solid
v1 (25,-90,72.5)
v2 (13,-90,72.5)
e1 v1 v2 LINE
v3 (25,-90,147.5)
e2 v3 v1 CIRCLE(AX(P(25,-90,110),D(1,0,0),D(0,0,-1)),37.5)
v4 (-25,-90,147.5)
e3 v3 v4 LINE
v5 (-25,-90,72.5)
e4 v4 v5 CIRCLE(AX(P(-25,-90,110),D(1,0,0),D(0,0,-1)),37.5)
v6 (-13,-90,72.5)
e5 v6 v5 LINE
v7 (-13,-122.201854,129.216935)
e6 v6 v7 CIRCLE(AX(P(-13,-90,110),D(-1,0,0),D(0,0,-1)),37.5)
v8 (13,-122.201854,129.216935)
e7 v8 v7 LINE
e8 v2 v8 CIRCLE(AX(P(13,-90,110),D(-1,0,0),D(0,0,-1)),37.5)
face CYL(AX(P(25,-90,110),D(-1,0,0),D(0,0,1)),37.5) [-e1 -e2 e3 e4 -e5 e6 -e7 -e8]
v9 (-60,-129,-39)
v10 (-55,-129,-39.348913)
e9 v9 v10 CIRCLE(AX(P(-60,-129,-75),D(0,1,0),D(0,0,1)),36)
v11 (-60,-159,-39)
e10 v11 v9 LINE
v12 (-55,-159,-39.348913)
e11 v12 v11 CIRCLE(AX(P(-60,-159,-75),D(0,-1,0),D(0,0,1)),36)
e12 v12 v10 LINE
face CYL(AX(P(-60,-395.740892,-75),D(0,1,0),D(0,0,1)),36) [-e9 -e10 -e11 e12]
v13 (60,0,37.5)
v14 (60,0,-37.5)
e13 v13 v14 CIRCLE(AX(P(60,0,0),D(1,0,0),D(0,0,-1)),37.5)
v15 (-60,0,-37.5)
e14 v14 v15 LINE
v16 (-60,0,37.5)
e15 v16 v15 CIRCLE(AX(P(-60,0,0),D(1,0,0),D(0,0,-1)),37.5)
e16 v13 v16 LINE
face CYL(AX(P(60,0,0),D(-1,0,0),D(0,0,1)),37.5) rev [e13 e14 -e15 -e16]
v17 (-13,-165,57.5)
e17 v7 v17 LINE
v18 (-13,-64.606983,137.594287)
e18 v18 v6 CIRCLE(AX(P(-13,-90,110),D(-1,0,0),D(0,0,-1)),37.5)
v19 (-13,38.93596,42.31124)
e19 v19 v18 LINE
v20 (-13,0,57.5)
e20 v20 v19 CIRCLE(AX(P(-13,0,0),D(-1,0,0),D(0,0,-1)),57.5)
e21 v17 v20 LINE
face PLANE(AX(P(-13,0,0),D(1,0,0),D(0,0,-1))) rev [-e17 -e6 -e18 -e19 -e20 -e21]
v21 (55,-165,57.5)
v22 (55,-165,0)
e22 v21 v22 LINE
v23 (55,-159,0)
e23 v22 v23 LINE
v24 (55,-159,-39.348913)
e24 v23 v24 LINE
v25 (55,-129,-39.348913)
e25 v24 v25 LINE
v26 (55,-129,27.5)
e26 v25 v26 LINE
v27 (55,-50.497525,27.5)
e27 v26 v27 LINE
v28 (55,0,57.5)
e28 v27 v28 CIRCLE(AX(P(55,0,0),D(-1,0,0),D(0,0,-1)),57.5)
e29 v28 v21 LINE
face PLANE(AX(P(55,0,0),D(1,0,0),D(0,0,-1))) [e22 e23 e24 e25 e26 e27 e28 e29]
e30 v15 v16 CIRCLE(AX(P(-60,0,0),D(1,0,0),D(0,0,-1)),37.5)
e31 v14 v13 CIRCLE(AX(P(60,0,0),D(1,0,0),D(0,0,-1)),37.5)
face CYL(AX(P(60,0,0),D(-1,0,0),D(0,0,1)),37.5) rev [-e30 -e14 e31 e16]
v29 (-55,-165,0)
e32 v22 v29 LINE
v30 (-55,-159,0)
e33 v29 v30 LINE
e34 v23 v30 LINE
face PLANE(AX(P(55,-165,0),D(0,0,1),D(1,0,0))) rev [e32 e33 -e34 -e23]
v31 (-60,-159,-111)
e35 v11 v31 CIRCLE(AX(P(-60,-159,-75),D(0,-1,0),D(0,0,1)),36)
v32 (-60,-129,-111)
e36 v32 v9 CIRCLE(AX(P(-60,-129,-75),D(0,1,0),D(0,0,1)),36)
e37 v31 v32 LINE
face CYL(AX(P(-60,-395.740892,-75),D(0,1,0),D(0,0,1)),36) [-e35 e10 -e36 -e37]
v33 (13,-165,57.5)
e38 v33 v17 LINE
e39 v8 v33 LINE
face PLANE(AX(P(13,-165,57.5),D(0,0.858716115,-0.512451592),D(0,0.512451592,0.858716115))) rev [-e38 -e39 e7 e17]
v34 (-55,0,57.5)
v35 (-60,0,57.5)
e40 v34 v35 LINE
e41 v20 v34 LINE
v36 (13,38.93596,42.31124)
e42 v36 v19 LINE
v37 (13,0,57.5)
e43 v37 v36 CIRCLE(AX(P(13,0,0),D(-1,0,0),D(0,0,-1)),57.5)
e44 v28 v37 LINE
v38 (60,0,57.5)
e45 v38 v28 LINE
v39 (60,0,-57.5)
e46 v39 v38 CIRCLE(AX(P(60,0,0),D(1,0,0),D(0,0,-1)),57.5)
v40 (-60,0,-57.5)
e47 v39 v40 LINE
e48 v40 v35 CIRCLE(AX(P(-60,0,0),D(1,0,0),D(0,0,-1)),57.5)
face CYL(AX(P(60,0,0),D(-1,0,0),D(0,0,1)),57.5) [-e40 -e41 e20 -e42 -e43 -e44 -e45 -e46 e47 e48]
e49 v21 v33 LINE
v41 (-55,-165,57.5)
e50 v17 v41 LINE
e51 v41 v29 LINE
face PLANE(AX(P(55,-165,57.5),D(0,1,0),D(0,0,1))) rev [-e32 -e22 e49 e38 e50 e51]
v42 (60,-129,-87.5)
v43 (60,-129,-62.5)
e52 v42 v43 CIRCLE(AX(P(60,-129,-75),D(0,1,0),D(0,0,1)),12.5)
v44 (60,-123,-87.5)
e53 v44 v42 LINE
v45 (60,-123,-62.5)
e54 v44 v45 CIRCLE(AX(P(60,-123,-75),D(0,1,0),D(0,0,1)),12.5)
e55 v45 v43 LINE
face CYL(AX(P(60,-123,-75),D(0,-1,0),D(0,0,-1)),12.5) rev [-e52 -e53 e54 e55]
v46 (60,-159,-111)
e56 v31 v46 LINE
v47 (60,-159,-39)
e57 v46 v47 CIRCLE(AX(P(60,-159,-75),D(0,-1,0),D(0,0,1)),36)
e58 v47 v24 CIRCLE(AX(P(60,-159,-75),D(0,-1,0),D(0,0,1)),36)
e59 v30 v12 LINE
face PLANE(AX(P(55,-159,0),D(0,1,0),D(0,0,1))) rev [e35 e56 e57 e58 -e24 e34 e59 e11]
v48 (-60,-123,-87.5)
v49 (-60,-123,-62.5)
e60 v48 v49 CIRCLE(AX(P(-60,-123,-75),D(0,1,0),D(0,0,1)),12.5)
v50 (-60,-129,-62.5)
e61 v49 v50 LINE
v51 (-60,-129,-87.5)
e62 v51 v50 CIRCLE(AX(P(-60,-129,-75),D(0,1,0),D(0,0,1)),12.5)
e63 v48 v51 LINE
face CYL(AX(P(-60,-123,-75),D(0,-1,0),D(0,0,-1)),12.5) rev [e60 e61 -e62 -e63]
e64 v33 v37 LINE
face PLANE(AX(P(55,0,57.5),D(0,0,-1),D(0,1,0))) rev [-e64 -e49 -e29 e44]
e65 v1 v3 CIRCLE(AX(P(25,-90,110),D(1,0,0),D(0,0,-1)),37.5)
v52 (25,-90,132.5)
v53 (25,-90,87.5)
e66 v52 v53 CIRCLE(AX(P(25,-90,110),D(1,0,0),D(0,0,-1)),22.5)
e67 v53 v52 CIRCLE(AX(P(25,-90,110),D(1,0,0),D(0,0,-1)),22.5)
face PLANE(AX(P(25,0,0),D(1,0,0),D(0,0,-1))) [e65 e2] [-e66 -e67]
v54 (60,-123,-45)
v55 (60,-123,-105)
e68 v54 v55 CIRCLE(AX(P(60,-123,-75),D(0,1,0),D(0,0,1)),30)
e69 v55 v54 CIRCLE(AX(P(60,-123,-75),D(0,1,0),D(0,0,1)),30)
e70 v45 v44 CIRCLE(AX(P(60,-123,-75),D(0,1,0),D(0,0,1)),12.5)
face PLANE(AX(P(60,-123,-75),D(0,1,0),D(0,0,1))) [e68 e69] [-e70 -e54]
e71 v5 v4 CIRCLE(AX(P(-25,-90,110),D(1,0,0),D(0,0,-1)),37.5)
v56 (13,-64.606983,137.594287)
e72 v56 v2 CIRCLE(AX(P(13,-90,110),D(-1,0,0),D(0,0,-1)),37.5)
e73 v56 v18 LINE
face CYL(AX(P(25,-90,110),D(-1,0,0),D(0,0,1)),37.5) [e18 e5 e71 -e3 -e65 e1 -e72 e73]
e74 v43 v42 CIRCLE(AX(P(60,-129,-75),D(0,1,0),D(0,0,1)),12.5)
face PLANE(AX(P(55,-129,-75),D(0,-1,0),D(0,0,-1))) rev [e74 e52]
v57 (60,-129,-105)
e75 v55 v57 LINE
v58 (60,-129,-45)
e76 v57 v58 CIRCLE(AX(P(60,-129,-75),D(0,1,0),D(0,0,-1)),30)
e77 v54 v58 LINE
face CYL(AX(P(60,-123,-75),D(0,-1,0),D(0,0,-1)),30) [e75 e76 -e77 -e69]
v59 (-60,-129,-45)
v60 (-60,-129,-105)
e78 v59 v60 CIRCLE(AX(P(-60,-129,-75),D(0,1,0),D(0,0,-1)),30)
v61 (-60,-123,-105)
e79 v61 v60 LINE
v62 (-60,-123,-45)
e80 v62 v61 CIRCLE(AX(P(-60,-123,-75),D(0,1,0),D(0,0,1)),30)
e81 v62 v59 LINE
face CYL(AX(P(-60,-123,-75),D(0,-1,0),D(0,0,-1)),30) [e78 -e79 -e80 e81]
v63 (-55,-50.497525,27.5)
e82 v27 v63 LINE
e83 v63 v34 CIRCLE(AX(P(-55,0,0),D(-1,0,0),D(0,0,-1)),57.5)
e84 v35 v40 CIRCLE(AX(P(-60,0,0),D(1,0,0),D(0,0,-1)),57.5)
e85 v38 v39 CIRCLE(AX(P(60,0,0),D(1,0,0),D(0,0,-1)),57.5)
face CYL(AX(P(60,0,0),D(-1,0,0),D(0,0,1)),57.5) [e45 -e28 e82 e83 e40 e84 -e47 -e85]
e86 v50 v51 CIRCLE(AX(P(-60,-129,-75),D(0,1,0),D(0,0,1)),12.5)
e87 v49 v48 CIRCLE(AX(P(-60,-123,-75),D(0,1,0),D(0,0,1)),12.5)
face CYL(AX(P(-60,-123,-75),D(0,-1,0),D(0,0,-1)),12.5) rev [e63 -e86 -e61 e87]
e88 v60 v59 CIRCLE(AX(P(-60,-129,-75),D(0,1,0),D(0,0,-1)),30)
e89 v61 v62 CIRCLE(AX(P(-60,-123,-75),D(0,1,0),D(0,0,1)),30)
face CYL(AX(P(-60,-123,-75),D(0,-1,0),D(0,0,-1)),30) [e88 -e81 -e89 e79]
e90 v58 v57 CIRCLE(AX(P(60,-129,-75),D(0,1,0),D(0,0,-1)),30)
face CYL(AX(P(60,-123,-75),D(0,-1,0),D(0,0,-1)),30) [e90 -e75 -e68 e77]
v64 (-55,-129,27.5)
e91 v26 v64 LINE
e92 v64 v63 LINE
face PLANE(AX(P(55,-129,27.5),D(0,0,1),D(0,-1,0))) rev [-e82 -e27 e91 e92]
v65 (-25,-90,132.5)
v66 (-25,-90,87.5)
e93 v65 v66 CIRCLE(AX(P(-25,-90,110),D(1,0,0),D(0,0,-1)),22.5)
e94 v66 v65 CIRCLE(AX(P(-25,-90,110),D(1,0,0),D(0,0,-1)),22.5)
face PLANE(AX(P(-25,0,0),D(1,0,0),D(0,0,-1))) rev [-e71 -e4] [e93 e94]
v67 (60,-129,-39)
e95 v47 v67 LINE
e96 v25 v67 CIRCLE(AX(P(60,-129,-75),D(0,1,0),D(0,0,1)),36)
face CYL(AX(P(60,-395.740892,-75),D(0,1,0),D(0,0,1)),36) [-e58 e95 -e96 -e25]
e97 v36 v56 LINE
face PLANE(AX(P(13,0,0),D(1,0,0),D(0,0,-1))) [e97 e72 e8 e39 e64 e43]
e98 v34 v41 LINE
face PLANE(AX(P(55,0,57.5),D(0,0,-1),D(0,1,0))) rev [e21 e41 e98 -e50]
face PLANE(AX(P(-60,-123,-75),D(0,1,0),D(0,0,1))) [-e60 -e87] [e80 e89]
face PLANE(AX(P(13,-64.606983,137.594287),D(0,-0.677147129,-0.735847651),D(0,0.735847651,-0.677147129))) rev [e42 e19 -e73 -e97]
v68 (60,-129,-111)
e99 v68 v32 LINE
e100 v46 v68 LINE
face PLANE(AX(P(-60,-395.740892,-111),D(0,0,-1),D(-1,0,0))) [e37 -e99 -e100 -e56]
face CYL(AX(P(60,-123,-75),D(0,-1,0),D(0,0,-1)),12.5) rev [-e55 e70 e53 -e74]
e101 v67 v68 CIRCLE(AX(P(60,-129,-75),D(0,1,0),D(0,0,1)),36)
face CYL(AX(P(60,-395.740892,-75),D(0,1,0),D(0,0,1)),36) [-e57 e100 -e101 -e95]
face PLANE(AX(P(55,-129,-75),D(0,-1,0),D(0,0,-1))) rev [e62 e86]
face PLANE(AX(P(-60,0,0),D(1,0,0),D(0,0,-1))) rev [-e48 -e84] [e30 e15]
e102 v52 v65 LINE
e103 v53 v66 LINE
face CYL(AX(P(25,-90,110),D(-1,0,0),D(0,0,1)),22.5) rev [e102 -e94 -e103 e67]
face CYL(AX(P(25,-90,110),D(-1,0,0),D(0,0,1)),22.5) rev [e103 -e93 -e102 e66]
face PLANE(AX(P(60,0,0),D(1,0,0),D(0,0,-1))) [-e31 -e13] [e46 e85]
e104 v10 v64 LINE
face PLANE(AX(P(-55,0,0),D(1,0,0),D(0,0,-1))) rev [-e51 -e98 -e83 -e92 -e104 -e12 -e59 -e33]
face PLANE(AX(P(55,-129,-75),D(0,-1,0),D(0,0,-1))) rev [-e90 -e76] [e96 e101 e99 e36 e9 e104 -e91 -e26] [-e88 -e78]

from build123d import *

# Parameters (mm, degrees)
BEARING_HOUSING_SKETCH_R   = 57.5
BEARING_HOUSING_SKETCH_R_2 = 37.5
BEARING_HOUSING_DEPTH      = 60
BRACKET_BODY_DEPTH         = 55
LOWER_BOSS_SKETCH_R        = 37.5
LOWER_BOSS_SKETCH_R_2      = 22.5
LOWER_BOSS_DEPTH           = 25
ANGLED_WEB_DEPTH           = 13
SIDE_LUG_DEPTH             = 30
SIDE_BOSS_SKETCH_R         = 30
SIDE_BOSS_SKETCH_R_2       = 12.5
SIDE_BOSS_DEPTH            = 6


with BuildPart() as part:
    # Bearing Housing Sketch → Bearing Housing (new, symmetric)
    with BuildSketch(Plane(origin=(0, 0, 0), x_dir=(0, 0, -1), z_dir=(1, 0, 0))):
        Circle(BEARING_HOUSING_SKETCH_R)
        Circle(BEARING_HOUSING_SKETCH_R_2, mode=Mode.SUBTRACT)
    extrude(amount=BEARING_HOUSING_DEPTH, both=True)

    # Bracket Body Sketch → Bracket Body (add, symmetric)
    with BuildSketch(Plane(origin=(0, 0, 0), x_dir=(0, 0, -1), z_dir=(1, 0, 0))):
        with BuildLine():
            Line((-57.5, 0), (-57.5, -165))
            Line((-57.5, -165), (0, -165))
            Line((0, -165), (0, -159))
            Line((0, -159), (75, -159))
            Line((75, -159), (75, -129))
            Line((75, -129), (-27.5, -129))
            Line((-27.5, -129), (-27.5, -50.497524692))
            ThreePointArc((-27.5, -50.497524692), (-49.434299833, -29.368350311), (-57.5, 0))
        make_face()
    extrude(amount=BRACKET_BODY_DEPTH, both=True)



with BuildPart() as body_2:
    # Lower Boss Sketch → Lower Boss (new, symmetric)
    with BuildSketch(Plane(origin=(0, 0, 0), x_dir=(0, 0, -1), z_dir=(1, 0, 0))):
        with Locations((-110, -90)):
            Circle(LOWER_BOSS_SKETCH_R)
        with Locations((-110, -90)):
            Circle(LOWER_BOSS_SKETCH_R_2, mode=Mode.SUBTRACT)
    extrude(amount=LOWER_BOSS_DEPTH, both=True)


with BuildPart() as part_1:
    add(part.part)

    add(body_2.part)  # Angled Web merges body 2
    # Angled Web Sketch → Angled Web (add, symmetric)
    with BuildSketch(Plane(origin=(0, 0, 0), x_dir=(0, 0, -1), z_dir=(1, 0, 0))):
        with BuildLine():
            Line((-57.5, 0), (-57.5, -165))
            Line((-57.5, -165), (-129.216934712, -122.201854299))
            ThreePointArc((-129.216934712, -122.201854299), (-72.890500848, -84.60230858), (-137.594286915, -64.606982659))
            Line((-137.594286915, -64.606982659), (-42.311239936, 38.935959922))
            ThreePointArc((-42.311239936, 38.935959922), (-53.568396916, 20.896814394), (-57.5, 0))
        make_face()
    extrude(amount=ANGLED_WEB_DEPTH, both=True)

    # Side Lug Sketch → Side Lug (add)
    with BuildSketch(Plane(origin=(0, -129, 0), x_dir=(1, 0, 0), z_dir=(0, 1, 0))):
        with BuildLine():
            Line((-60, 111), (60, 111))
            ThreePointArc((60, 111), (95.912665801, 72.493920376), (55, 39.34891306))
            Line((55, 39.34891306), (55, -27.5))
            Line((55, -27.5), (-55, -27.5))
            Line((-55, -27.5), (-55, 39.34891306))
            ThreePointArc((-55, 39.34891306), (-95.912665801, 72.493920376), (-60, 111))
        make_face()
    extrude(amount=-SIDE_LUG_DEPTH)

    # Side Boss Sketch → Side Boss (add)
    # profile 1 of 2: a face of its own
    with BuildSketch(Plane(origin=(0, -129, 0), x_dir=(1, 0, 0), z_dir=(0, 1, 0))):
        with Locations(Location((60, 75, 0), (0, 0, 90))):
            Circle(SIDE_BOSS_SKETCH_R)
        with Locations(Location((60, 75, 0), (0, 0, 270))):
            Circle(SIDE_BOSS_SKETCH_R_2, mode=Mode.SUBTRACT)
    # profile 2 of 2: a face of its own
    with BuildSketch(Plane(origin=(0, -129, 0), x_dir=(1, 0, 0), z_dir=(0, 1, 0))):
        with Locations(Location((-60, 75, 0), (0, 0, 90))):
            Circle(SIDE_BOSS_SKETCH_R)
        with Locations(Location((-60, 75, 0), (0, 0, 270))):
            Circle(SIDE_BOSS_SKETCH_R_2, mode=Mode.SUBTRACT)
    extrude(amount=SIDE_BOSS_DEPTH)


solid = part_1.part
